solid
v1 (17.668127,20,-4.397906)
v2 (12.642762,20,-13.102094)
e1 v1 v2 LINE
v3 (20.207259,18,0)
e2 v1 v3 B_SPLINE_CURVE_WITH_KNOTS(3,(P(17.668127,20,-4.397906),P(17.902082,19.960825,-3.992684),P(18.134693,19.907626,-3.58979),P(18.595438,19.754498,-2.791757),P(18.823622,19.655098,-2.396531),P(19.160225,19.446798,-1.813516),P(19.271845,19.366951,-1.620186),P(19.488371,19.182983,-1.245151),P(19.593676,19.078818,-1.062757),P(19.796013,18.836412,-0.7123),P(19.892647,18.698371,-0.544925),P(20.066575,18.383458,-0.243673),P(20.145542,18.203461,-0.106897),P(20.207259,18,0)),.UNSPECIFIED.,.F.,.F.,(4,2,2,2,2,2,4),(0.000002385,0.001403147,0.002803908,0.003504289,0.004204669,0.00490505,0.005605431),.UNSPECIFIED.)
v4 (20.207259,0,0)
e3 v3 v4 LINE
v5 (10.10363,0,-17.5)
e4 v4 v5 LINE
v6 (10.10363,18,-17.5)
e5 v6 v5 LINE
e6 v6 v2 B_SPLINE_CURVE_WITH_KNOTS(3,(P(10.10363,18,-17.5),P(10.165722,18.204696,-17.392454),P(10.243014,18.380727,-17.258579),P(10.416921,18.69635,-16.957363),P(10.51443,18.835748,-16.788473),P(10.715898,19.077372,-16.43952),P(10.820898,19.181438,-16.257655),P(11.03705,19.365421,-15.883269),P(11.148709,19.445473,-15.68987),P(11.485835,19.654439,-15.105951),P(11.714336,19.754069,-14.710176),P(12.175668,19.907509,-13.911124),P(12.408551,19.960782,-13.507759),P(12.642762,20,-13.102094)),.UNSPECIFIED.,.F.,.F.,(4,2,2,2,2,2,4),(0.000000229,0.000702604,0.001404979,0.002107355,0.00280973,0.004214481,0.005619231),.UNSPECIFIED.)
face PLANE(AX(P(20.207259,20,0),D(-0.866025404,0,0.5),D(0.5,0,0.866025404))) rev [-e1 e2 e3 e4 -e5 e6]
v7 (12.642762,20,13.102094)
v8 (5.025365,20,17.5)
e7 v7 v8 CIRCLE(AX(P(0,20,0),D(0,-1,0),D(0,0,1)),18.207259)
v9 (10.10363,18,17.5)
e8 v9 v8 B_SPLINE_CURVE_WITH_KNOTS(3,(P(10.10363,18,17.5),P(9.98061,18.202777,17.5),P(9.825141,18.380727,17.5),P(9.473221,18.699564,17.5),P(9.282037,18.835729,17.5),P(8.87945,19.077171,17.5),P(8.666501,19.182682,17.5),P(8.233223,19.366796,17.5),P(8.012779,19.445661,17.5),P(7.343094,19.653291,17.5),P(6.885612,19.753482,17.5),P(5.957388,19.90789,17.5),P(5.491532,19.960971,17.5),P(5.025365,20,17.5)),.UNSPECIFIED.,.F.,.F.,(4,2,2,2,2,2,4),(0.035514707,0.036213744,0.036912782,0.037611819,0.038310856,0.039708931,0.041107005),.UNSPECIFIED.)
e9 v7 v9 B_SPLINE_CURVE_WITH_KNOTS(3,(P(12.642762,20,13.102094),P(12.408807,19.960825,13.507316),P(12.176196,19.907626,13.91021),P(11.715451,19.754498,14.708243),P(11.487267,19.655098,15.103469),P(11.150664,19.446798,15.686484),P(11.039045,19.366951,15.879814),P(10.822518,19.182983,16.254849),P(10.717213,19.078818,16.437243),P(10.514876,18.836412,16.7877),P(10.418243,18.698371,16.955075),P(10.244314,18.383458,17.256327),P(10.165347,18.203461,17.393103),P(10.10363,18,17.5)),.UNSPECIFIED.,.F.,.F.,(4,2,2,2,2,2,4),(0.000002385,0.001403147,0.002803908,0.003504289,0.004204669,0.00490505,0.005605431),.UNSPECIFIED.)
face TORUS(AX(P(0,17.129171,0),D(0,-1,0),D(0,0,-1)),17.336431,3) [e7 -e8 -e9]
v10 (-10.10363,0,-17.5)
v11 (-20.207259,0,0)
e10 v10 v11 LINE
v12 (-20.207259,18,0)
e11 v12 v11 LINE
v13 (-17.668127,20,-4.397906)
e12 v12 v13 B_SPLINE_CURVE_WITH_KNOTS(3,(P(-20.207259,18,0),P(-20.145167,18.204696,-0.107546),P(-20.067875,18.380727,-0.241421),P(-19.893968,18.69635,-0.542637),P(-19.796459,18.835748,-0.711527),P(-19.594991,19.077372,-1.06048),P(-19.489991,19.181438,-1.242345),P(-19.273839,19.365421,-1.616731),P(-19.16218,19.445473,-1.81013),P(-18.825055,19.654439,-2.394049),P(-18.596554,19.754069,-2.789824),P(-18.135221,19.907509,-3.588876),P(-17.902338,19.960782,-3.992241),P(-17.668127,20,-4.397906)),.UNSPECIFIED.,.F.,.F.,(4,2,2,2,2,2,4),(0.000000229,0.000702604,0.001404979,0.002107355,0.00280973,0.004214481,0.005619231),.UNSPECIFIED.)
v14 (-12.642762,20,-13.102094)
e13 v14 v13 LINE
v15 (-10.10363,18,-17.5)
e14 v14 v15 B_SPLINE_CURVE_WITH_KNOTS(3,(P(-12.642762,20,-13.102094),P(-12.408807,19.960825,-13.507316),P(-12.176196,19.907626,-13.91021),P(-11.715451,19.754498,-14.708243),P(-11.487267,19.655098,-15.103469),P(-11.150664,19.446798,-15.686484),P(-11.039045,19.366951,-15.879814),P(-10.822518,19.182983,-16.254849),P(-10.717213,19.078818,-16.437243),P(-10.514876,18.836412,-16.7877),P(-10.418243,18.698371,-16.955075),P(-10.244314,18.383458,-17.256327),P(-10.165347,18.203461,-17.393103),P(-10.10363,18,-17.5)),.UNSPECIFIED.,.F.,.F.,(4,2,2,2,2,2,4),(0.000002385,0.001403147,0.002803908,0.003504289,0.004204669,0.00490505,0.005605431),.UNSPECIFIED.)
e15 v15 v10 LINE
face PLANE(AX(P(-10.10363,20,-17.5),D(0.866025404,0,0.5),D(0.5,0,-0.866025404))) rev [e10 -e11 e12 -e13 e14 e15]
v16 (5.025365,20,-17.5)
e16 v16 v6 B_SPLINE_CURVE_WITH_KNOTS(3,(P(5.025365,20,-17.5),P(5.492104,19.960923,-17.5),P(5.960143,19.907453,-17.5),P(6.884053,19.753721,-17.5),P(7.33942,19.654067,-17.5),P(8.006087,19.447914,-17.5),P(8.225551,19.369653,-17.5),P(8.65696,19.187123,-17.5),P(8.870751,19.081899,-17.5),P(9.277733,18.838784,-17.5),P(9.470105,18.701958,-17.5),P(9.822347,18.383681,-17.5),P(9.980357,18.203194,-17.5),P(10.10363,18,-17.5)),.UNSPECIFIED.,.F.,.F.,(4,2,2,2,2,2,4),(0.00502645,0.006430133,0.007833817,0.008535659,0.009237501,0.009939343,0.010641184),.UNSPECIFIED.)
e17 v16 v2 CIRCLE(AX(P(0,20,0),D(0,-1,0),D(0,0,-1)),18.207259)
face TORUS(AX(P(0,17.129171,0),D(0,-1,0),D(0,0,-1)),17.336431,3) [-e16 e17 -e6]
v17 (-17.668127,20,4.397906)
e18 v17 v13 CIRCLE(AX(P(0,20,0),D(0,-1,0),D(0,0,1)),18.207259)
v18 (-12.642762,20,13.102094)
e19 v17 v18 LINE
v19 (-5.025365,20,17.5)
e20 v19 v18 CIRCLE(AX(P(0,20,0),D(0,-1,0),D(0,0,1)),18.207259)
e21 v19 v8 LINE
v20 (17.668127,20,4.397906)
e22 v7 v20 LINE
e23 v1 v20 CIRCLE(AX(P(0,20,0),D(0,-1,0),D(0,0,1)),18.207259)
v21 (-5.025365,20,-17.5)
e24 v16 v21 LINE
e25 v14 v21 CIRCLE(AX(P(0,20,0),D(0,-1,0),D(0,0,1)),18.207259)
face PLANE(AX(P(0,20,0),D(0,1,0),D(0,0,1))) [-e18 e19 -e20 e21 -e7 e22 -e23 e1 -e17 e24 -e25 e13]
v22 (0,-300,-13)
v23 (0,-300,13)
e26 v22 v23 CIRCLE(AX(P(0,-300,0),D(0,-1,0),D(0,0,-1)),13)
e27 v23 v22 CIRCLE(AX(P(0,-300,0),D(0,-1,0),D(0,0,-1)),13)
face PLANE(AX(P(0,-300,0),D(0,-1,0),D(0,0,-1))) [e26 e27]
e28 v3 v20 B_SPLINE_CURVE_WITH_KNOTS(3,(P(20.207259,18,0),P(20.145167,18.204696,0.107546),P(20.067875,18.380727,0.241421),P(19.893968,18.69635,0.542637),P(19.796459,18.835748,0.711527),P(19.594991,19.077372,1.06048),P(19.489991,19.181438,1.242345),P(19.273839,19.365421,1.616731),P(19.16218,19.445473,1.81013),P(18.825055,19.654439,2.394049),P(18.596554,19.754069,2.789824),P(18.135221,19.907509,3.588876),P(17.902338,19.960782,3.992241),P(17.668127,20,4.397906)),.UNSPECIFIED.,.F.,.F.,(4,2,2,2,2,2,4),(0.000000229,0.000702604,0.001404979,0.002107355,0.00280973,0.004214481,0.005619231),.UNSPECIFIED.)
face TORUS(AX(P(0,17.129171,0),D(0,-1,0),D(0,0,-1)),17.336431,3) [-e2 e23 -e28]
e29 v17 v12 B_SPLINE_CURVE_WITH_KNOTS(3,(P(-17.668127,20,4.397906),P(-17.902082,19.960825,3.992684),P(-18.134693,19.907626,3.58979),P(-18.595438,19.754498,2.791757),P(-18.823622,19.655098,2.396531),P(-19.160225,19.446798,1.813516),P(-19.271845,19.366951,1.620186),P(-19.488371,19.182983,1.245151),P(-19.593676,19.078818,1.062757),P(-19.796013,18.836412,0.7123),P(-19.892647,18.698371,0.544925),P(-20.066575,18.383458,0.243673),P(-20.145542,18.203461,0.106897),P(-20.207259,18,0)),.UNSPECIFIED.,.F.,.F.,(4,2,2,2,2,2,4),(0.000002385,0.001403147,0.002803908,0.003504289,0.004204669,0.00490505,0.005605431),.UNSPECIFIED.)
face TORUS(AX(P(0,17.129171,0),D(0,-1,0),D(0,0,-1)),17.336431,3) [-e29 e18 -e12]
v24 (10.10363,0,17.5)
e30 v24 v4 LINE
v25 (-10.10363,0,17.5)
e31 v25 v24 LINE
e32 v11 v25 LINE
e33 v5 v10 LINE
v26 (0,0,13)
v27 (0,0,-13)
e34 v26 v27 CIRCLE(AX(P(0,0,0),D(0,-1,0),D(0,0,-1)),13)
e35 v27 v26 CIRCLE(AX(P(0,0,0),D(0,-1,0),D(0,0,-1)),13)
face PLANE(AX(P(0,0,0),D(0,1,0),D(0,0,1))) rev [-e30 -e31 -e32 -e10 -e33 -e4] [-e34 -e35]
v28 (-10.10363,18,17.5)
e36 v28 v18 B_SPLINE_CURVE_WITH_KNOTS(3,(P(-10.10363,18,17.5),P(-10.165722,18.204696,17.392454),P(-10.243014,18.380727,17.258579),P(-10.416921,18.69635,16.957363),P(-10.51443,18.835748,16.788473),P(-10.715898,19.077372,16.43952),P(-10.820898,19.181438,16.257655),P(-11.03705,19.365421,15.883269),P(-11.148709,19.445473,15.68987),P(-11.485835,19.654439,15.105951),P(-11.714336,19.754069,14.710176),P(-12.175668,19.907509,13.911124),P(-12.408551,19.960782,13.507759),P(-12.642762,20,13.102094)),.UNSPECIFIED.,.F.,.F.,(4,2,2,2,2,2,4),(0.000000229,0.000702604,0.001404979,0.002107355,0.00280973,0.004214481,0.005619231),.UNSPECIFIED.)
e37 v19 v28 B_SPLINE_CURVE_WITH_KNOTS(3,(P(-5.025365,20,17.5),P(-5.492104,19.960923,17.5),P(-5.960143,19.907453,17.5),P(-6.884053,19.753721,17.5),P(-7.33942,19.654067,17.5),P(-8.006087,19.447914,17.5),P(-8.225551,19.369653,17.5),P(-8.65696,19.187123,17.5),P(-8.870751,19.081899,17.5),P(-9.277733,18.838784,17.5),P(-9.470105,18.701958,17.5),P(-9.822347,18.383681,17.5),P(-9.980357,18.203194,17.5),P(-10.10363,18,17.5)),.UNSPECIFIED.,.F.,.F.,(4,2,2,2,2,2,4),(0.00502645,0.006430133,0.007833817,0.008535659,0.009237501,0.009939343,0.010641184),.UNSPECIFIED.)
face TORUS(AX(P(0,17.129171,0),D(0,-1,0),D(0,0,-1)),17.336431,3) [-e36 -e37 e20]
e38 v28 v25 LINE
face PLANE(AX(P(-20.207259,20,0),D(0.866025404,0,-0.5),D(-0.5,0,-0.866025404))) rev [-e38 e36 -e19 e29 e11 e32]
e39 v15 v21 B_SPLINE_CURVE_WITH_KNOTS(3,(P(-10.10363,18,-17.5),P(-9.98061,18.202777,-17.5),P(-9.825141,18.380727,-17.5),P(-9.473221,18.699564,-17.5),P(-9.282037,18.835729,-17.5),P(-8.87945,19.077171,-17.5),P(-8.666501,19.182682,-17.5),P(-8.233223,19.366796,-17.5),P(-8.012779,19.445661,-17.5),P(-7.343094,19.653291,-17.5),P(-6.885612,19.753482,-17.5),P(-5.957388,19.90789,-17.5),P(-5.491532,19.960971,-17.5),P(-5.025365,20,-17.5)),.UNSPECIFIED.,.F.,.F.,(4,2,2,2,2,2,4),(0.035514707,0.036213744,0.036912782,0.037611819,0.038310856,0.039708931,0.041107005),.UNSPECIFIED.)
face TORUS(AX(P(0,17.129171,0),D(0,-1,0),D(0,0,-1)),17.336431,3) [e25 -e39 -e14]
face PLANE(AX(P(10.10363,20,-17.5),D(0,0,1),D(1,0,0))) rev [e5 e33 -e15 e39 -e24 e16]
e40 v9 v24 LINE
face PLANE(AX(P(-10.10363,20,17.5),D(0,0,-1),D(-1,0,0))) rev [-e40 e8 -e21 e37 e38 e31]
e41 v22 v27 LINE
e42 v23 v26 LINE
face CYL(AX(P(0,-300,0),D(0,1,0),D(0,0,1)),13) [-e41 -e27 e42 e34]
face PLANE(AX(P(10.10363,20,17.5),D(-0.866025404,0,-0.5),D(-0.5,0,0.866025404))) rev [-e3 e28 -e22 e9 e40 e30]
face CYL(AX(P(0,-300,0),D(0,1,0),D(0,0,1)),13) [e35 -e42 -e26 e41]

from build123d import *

# Parameters (mm, degrees)
HEX_HEAD_DEPTH     = 20
SHANK_PROFILE_26_R = 13
SHANK_26X300_DEPTH = 300


with BuildPart() as part:
    # Hex Head Profile 35AF → Hex Head (new body)
    with BuildSketch(Plane(origin=(0, 0, 0), x_dir=(1, 0, 0), z_dir=(0, 1, 0))):
        Polygon((20.207259422, 0), (10.103629711, 17.5), (-10.103629711, 17.5), (-20.207259422, 0), (-10.103629711, -17.5), (10.103629711, -17.5), align=None)
    extrude(amount=HEX_HEAD_DEPTH)

    # Shank Profile Ø26 → Shank Ø26x300 (add)
    with BuildSketch(Plane.XZ):
        with Locations(Location((0, 0, 0), (0, 0, 270))):
            Circle(SHANK_PROFILE_26_R)
    extrude(amount=SHANK_26X300_DEPTH)

    # Head Chamfer Profile → Head Chamfer (revolve, cut)
    with BuildSketch(Plane.XY):
        with BuildLine():
            Line((18.207259422, 20), (20.207259422, 20))
            Line((20.207259422, 20), (20.207259422, 18))
            ThreePointArc((20.207259422, 18), (19.457751072, 19.25049165), (18.207259422, 20))
        make_face()
    revolve(axis=Axis((0, 0, 0), (0, 1, 0)), mode=Mode.SUBTRACT)


solid = part.part
